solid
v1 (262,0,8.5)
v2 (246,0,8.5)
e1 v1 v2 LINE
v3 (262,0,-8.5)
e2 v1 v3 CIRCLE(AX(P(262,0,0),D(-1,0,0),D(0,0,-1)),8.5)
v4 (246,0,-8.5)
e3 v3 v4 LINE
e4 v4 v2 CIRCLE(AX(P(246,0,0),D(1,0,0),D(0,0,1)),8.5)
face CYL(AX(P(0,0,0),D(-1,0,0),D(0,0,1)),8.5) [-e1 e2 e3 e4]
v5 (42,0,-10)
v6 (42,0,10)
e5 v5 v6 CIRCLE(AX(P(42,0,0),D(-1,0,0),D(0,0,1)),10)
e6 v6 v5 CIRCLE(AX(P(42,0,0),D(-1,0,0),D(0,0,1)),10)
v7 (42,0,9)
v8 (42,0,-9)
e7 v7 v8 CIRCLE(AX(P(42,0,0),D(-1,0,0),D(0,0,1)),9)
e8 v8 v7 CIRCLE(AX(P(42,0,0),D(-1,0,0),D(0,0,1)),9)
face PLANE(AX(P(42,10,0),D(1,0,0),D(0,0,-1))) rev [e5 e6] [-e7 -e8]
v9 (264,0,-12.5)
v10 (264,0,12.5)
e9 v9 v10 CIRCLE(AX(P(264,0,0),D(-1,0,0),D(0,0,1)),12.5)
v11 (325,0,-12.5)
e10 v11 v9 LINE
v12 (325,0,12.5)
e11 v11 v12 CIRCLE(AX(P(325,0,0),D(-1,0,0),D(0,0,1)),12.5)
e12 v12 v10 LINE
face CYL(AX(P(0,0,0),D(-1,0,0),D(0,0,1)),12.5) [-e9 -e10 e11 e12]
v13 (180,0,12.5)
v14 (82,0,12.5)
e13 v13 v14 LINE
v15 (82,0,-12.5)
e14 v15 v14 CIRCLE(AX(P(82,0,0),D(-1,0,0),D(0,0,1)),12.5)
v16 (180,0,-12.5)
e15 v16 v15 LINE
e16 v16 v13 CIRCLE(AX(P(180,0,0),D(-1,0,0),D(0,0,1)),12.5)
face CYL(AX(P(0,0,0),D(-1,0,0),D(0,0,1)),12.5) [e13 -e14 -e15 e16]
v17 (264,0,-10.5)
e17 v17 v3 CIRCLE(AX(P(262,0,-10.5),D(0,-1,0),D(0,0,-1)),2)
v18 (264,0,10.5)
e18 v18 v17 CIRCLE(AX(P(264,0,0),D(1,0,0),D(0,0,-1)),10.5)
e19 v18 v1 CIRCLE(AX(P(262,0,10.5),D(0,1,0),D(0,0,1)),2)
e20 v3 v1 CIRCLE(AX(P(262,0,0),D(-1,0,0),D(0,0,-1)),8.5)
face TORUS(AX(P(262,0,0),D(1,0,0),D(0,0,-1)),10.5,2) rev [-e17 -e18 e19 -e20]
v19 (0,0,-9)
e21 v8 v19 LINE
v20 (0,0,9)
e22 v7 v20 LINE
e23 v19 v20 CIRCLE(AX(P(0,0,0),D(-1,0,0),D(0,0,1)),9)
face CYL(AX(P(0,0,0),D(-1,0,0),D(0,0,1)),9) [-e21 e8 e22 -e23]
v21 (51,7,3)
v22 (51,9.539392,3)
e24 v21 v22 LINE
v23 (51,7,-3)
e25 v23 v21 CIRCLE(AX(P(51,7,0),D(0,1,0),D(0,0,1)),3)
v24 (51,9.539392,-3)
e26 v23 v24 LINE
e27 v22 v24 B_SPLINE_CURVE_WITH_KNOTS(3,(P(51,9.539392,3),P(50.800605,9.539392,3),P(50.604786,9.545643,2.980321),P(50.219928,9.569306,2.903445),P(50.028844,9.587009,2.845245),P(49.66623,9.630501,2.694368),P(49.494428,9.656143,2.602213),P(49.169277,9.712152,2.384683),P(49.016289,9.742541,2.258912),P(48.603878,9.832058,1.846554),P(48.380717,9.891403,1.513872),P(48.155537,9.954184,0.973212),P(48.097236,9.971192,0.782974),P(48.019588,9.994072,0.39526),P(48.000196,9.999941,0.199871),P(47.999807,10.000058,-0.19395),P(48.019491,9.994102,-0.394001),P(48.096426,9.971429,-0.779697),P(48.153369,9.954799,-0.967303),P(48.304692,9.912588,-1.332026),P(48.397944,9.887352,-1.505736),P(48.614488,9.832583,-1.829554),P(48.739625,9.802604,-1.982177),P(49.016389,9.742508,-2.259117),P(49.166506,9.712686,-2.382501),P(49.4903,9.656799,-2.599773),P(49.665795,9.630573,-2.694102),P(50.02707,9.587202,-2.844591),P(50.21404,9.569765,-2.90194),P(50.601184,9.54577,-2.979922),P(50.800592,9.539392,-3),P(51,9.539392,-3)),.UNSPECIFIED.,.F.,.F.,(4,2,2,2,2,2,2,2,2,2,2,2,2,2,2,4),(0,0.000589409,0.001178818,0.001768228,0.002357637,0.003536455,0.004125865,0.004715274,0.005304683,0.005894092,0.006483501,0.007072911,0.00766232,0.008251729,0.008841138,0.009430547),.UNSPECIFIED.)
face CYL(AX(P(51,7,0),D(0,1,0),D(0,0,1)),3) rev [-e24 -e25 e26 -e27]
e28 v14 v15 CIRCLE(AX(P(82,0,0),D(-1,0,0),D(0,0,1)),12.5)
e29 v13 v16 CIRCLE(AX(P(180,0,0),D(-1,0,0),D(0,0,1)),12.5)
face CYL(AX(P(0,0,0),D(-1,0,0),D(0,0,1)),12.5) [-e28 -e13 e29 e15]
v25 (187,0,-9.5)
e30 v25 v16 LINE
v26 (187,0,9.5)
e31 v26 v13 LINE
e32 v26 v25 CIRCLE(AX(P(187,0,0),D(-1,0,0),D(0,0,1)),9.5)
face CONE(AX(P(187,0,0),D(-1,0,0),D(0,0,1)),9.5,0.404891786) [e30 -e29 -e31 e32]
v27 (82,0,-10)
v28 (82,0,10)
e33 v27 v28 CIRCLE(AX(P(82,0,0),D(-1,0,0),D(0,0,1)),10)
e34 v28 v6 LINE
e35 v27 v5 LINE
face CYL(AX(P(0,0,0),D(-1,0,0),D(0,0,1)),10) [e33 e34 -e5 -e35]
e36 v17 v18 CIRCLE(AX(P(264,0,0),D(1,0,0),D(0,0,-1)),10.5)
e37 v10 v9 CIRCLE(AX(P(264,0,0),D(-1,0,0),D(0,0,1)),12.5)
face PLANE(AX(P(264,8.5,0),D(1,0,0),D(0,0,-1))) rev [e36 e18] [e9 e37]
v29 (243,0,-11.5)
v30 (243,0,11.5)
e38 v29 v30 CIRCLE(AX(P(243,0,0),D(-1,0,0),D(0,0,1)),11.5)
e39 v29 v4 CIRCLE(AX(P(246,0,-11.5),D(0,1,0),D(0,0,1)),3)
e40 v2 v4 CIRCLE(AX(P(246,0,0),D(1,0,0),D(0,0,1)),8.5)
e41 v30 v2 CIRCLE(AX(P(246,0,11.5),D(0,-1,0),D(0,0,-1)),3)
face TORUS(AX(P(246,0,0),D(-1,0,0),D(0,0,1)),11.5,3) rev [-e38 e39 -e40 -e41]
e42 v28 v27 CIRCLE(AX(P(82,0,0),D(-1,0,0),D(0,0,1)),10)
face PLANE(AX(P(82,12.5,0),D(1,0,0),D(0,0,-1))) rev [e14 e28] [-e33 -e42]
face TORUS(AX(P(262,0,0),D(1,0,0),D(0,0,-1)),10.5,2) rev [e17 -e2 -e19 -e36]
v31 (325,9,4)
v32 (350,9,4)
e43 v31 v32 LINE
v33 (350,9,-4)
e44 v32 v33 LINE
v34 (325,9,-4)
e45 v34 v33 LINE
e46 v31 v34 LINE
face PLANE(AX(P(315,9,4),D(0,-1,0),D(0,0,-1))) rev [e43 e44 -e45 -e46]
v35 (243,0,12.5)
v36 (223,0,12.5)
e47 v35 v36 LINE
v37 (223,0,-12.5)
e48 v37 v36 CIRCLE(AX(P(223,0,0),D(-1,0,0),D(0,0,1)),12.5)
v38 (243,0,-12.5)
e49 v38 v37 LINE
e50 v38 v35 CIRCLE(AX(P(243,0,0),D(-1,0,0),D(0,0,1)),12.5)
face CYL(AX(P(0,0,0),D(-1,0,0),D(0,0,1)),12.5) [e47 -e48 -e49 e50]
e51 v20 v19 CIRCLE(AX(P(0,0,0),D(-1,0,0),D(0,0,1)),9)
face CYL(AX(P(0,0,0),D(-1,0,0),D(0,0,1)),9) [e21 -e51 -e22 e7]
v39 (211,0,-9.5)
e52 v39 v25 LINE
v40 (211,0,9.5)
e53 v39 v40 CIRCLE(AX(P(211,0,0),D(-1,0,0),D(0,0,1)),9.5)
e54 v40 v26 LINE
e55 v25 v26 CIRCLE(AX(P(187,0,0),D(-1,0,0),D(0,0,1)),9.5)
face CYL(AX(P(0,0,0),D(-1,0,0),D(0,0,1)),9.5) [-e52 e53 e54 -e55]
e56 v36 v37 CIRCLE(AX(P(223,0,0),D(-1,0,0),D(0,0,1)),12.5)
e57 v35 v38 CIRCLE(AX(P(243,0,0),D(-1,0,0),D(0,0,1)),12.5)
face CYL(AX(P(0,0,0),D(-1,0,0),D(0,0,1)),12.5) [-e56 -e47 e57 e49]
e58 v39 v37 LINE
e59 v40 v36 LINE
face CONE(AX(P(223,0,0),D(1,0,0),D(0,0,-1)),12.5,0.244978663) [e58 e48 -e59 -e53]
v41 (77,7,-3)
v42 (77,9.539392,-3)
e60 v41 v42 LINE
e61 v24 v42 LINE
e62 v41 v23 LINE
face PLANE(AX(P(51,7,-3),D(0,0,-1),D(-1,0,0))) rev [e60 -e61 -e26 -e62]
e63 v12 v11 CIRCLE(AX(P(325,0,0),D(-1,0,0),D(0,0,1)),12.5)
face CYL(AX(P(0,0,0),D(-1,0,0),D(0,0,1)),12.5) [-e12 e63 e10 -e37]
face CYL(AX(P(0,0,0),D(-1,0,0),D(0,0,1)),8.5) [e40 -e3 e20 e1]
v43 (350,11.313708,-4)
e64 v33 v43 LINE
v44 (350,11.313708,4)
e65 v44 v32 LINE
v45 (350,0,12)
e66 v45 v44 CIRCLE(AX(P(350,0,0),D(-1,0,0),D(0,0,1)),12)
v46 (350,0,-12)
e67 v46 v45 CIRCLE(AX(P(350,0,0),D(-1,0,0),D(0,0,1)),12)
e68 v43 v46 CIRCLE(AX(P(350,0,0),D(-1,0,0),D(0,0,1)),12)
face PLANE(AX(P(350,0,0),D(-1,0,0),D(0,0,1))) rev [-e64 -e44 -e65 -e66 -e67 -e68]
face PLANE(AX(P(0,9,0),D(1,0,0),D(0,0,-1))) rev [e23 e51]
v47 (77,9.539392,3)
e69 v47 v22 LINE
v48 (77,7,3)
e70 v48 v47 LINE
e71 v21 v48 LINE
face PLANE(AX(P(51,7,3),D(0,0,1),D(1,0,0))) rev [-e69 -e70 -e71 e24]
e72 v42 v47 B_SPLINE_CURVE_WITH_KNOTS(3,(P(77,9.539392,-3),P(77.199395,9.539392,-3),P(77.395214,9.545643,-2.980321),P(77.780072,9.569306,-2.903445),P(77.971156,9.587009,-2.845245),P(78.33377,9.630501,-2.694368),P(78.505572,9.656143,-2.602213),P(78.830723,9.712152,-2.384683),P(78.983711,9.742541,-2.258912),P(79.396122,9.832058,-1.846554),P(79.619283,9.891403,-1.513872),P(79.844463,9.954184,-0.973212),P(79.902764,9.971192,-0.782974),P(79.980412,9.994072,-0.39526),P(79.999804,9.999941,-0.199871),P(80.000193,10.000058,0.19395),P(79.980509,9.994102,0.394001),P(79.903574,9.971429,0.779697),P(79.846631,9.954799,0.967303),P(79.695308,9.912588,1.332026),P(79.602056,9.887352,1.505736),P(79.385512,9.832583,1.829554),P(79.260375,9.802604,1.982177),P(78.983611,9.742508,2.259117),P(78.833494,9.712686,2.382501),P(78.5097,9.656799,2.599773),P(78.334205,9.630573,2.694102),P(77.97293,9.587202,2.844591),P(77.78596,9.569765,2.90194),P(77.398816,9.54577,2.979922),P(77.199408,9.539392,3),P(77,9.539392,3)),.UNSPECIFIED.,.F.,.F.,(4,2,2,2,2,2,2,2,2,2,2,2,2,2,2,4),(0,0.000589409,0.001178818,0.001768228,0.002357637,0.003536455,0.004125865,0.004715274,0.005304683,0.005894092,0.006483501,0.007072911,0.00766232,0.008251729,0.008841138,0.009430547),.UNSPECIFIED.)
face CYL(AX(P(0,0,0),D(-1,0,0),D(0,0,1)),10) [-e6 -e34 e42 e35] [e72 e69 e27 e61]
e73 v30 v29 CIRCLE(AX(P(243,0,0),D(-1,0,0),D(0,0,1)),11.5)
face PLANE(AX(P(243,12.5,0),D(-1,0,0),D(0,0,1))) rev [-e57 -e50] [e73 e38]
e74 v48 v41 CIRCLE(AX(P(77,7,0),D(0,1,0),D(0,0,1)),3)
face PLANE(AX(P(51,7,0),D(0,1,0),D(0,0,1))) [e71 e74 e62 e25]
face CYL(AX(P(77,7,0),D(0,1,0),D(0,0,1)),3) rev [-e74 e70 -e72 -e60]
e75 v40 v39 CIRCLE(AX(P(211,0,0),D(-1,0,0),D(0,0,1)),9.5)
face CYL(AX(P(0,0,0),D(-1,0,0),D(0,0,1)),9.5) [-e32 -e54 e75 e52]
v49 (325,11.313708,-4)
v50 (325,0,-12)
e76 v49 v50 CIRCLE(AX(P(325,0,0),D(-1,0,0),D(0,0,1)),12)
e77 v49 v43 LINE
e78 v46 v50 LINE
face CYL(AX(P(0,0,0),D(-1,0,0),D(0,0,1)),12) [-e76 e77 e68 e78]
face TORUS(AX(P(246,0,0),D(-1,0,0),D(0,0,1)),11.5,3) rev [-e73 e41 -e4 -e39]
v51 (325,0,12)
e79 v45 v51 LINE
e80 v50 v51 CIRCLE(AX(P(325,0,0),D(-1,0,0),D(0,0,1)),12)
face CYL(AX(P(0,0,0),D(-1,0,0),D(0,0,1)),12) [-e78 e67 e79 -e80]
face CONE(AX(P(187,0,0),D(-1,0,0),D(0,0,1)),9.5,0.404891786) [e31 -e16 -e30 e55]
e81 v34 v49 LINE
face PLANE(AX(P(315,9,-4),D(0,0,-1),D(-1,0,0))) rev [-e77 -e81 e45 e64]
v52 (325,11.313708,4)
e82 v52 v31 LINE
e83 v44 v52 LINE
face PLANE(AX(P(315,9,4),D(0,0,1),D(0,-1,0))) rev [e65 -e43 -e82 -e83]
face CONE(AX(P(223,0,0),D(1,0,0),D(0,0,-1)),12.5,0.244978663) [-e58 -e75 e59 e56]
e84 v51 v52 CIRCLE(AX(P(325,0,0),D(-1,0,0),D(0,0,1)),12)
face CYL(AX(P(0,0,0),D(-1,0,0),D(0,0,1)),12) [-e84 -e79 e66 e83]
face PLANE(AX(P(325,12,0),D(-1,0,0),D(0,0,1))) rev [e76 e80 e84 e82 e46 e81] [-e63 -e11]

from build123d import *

# Parameters (mm, degrees)
SHOULDER_FILLET_R2_R    = 2
SHOULDER_FILLET_R3_R    = 3
KEYWAY_A_SKETCH_W       = 8
KEYWAY_A_SKETCH_H       = 6
KEYWAY_A_CUT_DEPTH      = 25
KEYWAY_START            = 10
KEYWAY_B_CUT_26X3_DEPTH = 3


with BuildPart() as part:
    # Shaft Profile Sketch → Shaft Body Revolve (revolve)
    with BuildSketch(Plane.XY, mode=Mode.PRIVATE) as shaft_body_revolve_sk:
        Polygon((0, 0), (350, 0), (350, 12), (325, 12), (325, 12.5), (264, 12.5), (264, 8.5), (243, 8.5), (243, 12.5), (223, 12.5), (211, 9.5), (187, 9.5), (180, 12.5), (82, 12.5), (82, 10), (42, 10), (42, 9), (0, 9), align=None)
    revolve(shaft_body_revolve_sk.sketch.rotate(Axis((0, 0, 0), (1, 0, 0)), 90), axis=Axis((0, 0, 0), (1, 0, 0)))

    # Shoulder Fillet R2
    shoulder_fillet_r2_edges = [part.edges().sort_by_distance(p)[0] for p in [
        (264, 0, -8.5),
    ]]
    fillet(shoulder_fillet_r2_edges, radius=SHOULDER_FILLET_R2_R)

    # Shoulder Fillet R3
    shoulder_fillet_r3_edges = [part.edges().sort_by_distance(p)[0] for p in [
        (243, 0, -8.5),
    ]]
    fillet(shoulder_fillet_r3_edges, radius=SHOULDER_FILLET_R3_R)

    # Keyway A Sketch → Keyway A Cut (cut)
    with BuildSketch(Plane(origin=(350, 0, 0), x_dir=(0, 0, -1), z_dir=(1, 0, 0))):
        with Locations((0, 12)):
            Rectangle(KEYWAY_A_SKETCH_W, KEYWAY_A_SKETCH_H)
    extrude(amount=-KEYWAY_A_CUT_DEPTH, mode=Mode.SUBTRACT)

    # Keyway B Sketch 26x3 → Keyway B Cut 26x3 (cut)
    with BuildSketch(Plane(origin=(0, 0, 0), x_dir=(1, 0, 0), z_dir=(0, 1, 0)).offset(KEYWAY_START)):
        with BuildLine():
            Line((51, 3), (77, 3))
            ThreePointArc((77, 3), (80, 0), (77, -3))
            Line((77, -3), (51, -3))
            ThreePointArc((51, -3), (48, 0), (51, 3))
        make_face()
    extrude(amount=-KEYWAY_B_CUT_26X3_DEPTH, mode=Mode.SUBTRACT)


solid = part.part
